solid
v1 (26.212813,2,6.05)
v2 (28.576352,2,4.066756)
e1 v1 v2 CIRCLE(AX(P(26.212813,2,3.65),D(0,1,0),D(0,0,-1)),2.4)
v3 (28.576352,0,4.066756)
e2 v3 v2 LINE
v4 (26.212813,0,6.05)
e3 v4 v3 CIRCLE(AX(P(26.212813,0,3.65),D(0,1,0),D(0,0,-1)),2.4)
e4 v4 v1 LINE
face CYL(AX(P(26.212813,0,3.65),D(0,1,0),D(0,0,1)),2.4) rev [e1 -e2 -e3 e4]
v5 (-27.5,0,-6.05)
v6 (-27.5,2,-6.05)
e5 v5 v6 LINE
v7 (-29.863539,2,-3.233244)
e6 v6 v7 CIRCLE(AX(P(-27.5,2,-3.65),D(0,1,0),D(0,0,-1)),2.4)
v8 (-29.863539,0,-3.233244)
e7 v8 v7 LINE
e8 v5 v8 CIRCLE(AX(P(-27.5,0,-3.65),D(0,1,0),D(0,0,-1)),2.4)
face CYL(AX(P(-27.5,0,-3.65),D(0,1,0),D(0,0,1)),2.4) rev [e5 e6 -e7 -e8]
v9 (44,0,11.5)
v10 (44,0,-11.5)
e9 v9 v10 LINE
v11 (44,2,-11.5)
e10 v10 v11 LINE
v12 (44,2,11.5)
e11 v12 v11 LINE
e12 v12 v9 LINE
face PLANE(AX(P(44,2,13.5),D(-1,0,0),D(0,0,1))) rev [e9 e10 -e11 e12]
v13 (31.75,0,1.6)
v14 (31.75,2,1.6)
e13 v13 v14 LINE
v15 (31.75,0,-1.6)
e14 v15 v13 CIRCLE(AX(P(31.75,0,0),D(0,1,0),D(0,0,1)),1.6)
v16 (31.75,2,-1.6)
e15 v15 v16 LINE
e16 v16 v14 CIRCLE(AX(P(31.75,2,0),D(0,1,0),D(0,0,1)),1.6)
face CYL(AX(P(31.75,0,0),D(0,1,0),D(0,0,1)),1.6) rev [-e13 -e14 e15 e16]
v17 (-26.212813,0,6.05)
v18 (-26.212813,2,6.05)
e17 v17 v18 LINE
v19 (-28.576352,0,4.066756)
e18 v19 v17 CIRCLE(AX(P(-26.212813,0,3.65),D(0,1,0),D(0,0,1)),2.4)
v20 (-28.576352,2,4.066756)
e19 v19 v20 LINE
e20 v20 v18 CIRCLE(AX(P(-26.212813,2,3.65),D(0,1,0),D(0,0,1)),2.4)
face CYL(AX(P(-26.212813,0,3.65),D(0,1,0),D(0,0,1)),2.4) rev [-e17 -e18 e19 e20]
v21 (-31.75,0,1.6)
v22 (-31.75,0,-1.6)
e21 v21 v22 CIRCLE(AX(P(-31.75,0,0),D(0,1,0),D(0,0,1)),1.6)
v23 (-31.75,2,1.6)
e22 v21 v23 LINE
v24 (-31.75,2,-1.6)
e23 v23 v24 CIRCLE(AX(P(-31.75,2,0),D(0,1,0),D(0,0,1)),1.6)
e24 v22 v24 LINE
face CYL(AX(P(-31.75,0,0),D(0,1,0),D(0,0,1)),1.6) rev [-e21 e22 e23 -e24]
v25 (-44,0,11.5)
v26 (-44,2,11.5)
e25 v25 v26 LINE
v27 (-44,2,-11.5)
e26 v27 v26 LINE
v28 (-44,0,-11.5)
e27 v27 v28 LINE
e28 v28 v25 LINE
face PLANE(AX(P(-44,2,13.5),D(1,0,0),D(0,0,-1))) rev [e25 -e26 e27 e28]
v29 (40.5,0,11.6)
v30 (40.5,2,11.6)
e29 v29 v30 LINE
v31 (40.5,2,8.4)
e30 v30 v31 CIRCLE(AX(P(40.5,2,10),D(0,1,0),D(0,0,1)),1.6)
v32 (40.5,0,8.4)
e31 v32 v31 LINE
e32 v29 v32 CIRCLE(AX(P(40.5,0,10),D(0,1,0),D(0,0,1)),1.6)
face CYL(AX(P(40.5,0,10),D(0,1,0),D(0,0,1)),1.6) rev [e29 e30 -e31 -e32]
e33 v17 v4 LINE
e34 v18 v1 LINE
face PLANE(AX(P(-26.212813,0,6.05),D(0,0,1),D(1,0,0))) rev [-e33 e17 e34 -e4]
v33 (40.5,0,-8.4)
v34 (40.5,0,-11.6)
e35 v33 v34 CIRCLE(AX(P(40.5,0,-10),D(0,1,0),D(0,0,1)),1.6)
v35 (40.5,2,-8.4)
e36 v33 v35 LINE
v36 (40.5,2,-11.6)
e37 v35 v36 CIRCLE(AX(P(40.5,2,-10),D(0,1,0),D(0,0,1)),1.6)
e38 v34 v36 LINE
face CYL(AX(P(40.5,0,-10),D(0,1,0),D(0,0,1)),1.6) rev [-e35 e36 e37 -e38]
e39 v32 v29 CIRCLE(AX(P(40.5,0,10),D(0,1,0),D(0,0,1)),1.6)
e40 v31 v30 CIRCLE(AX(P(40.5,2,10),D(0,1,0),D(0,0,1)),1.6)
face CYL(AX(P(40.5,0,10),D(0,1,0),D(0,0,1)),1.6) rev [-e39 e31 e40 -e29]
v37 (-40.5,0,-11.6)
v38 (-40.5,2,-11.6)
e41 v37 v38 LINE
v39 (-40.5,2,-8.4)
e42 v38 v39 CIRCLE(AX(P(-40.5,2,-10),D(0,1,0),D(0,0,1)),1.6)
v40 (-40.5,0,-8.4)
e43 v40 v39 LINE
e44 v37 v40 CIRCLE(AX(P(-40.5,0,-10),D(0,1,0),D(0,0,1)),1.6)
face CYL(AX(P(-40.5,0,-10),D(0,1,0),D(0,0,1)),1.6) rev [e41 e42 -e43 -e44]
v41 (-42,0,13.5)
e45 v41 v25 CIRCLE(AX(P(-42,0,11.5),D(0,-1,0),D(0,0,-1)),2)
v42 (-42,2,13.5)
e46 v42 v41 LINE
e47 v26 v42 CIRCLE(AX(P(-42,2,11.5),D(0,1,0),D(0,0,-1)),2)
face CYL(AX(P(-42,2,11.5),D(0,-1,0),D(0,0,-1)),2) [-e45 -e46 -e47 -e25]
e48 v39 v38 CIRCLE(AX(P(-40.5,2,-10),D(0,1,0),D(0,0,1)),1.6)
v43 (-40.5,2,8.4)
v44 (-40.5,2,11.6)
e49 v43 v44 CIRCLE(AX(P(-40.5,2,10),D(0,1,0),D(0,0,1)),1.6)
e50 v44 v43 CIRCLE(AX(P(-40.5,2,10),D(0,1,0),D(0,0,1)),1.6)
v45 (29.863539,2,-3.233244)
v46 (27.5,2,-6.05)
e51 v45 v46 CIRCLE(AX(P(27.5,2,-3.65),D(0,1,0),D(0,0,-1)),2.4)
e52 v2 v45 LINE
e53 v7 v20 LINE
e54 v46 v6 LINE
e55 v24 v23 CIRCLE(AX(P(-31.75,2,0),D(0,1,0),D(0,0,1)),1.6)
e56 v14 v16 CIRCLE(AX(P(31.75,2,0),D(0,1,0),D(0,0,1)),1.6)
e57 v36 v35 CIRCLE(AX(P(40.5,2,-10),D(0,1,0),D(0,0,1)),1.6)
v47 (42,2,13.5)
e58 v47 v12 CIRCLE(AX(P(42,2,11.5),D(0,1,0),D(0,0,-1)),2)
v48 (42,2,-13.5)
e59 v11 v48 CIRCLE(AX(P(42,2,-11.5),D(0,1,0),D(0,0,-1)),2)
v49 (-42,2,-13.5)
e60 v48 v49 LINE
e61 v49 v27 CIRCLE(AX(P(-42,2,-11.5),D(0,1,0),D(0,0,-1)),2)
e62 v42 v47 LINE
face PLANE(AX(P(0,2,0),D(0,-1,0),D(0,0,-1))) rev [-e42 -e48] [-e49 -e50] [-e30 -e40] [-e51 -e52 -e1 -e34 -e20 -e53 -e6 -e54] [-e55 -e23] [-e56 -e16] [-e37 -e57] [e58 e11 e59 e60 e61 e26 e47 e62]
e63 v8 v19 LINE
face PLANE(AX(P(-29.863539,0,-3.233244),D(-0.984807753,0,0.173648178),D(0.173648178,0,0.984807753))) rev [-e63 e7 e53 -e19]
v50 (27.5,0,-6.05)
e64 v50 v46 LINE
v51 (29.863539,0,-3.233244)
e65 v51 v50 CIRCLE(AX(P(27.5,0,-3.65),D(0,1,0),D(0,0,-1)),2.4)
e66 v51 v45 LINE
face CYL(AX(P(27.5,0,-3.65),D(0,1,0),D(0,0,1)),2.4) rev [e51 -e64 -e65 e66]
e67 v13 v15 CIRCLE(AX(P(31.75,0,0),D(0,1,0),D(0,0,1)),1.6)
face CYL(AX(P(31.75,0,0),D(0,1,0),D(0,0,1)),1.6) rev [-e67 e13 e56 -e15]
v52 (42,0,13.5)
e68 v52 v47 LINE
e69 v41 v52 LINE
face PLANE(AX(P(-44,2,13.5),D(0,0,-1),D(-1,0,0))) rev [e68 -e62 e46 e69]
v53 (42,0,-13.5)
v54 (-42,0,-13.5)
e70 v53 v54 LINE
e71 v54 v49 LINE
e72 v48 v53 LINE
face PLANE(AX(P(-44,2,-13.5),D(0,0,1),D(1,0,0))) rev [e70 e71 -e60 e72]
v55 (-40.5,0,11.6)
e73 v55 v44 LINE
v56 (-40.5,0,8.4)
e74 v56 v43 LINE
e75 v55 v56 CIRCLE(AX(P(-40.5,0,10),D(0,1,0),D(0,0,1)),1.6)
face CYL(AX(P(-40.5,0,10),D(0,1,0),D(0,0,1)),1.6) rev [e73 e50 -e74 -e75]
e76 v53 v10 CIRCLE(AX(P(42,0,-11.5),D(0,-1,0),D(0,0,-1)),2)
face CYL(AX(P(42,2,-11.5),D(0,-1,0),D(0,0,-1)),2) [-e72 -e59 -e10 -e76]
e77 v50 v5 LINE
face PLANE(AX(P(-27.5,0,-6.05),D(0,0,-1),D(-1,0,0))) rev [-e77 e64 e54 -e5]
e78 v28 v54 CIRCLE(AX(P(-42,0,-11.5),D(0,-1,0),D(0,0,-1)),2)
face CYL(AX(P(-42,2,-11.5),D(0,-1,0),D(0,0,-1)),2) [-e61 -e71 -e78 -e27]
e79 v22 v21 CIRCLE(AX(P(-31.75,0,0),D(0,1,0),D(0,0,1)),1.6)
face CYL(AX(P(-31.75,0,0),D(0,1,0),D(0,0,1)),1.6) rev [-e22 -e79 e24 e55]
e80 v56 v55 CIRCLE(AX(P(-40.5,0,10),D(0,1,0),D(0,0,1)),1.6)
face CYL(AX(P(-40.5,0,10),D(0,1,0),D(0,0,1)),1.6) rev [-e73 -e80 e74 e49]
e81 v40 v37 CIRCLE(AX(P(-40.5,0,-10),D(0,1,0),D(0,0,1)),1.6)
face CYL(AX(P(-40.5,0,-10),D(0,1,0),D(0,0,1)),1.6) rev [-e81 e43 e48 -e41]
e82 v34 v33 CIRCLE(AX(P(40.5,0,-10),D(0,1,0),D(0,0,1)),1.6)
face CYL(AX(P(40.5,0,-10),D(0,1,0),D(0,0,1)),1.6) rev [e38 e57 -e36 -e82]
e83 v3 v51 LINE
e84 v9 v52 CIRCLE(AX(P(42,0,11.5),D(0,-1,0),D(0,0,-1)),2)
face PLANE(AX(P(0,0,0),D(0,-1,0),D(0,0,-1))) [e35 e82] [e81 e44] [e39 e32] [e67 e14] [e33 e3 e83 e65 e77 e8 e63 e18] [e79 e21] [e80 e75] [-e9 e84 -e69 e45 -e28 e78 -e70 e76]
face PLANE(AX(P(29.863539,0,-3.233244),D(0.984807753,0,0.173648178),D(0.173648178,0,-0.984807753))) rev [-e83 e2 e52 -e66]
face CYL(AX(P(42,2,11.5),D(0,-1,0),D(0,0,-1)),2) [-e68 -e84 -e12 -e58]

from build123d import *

# Parameters (mm, degrees)
SKETCH1_W           = 88
SKETCH1_H           = 27
BOSS_EXTRUDE1_DEPTH = 2
SKETCH2_R           = 1.6
CUT_EXTRUDE1_DEPTH  = 47.067884692
FILLET1_R           = 2
CUT_EXTRUDE2_DEPTH  = 47.067884692
M3_TAPPED_HOLE1_D   = 2.5
SKETCH6_R           = 1.6
CUT_EXTRUDE3_DEPTH  = 47.067884692


with BuildPart() as part:
    # Sketch1 → Boss-Extrude1 (new body)
    with BuildSketch(Plane(origin=(0, 0, 0), x_dir=(1, 0, 0), z_dir=(0, 1, 0))):
        Rectangle(SKETCH1_W, SKETCH1_H)
    extrude(amount=BOSS_EXTRUDE1_DEPTH)

    # Sketch2 → Cut-Extrude1 (cut, through all)
    with BuildSketch(Plane(origin=(0, 2, 0), x_dir=(1, 0, 0), z_dir=(0, 1, 0))):
        with Locations(Location((-40.5, 10, 0), (0, 0, 270))):
            Circle(SKETCH2_R)
        with Locations(Location((40.5, 10, 0), (0, 0, 270))):
            Circle(SKETCH2_R)
        with Locations(Location((40.5, -10, 0), (0, 0, 270))):
            Circle(SKETCH2_R)
        with Locations(Location((-40.5, -10, 0), (0, 0, 270))):
            Circle(SKETCH2_R)
    extrude(amount=-CUT_EXTRUDE1_DEPTH, mode=Mode.SUBTRACT)

    # Fillet1
    fillet1_edges = [part.edges().sort_by_distance(p)[0] for p in [
        (44, 1, 13.5),
        (-44, 1, 13.5),
        (-44, 1, -13.5),
        (44, 1, -13.5),
    ]]
    fillet(fillet1_edges, radius=FILLET1_R)

    # Sketch3 → Cut-Extrude2 (cut, through all)
    with BuildSketch(Plane(origin=(0, 2, 0), x_dir=(1, 0, 0), z_dir=(0, 1, 0))):
        with BuildLine():
            Line((-29.863538607, 3.233244374), (-28.576351648, -4.066755626))
            ThreePointArc((-28.576351648, -4.066755626), (-27.755503304, -5.488506663), (-26.212813041, -6.05))
            Line((-26.212813041, -6.05), (26.212813041, -6.05))
            ThreePointArc((26.212813041, -6.05), (27.755503304, -5.488506663), (28.576351648, -4.066755626))
            Line((28.576351648, -4.066755626), (29.863538607, 3.233244374))
            ThreePointArc((29.863538607, 3.233244374), (29.338506663, 5.192690263), (27.5, 6.05))
            Line((27.5, 6.05), (-27.5, 6.05))
            ThreePointArc((-27.5, 6.05), (-29.338506663, 5.192690263), (-29.863538607, 3.233244374))
        make_face()
    extrude(amount=-CUT_EXTRUDE2_DEPTH, mode=Mode.SUBTRACT)

    # M3 Tapped Hole1 (through all)
    with Locations(Plane(origin=(0, 2, 0), x_dir=(1, 0, 0), z_dir=(0, 1, 0))):
        with Locations((-31.75, 0), (31.75, 0)):
            Hole(M3_TAPPED_HOLE1_D / 2)

    # Sketch6 → Cut-Extrude3 (cut, through all)
    with BuildSketch(Plane(origin=(0, 2, 0), x_dir=(1, 0, 0), z_dir=(0, 1, 0))):
        with Locations(Location((-31.75, 0, 0), (0, 0, 270))):
            Circle(SKETCH6_R)
        with Locations(Location((31.75, 0, 0), (0, 0, 270))):
            Circle(SKETCH6_R)
    extrude(amount=-CUT_EXTRUDE3_DEPTH, mode=Mode.SUBTRACT)


solid = part.part
